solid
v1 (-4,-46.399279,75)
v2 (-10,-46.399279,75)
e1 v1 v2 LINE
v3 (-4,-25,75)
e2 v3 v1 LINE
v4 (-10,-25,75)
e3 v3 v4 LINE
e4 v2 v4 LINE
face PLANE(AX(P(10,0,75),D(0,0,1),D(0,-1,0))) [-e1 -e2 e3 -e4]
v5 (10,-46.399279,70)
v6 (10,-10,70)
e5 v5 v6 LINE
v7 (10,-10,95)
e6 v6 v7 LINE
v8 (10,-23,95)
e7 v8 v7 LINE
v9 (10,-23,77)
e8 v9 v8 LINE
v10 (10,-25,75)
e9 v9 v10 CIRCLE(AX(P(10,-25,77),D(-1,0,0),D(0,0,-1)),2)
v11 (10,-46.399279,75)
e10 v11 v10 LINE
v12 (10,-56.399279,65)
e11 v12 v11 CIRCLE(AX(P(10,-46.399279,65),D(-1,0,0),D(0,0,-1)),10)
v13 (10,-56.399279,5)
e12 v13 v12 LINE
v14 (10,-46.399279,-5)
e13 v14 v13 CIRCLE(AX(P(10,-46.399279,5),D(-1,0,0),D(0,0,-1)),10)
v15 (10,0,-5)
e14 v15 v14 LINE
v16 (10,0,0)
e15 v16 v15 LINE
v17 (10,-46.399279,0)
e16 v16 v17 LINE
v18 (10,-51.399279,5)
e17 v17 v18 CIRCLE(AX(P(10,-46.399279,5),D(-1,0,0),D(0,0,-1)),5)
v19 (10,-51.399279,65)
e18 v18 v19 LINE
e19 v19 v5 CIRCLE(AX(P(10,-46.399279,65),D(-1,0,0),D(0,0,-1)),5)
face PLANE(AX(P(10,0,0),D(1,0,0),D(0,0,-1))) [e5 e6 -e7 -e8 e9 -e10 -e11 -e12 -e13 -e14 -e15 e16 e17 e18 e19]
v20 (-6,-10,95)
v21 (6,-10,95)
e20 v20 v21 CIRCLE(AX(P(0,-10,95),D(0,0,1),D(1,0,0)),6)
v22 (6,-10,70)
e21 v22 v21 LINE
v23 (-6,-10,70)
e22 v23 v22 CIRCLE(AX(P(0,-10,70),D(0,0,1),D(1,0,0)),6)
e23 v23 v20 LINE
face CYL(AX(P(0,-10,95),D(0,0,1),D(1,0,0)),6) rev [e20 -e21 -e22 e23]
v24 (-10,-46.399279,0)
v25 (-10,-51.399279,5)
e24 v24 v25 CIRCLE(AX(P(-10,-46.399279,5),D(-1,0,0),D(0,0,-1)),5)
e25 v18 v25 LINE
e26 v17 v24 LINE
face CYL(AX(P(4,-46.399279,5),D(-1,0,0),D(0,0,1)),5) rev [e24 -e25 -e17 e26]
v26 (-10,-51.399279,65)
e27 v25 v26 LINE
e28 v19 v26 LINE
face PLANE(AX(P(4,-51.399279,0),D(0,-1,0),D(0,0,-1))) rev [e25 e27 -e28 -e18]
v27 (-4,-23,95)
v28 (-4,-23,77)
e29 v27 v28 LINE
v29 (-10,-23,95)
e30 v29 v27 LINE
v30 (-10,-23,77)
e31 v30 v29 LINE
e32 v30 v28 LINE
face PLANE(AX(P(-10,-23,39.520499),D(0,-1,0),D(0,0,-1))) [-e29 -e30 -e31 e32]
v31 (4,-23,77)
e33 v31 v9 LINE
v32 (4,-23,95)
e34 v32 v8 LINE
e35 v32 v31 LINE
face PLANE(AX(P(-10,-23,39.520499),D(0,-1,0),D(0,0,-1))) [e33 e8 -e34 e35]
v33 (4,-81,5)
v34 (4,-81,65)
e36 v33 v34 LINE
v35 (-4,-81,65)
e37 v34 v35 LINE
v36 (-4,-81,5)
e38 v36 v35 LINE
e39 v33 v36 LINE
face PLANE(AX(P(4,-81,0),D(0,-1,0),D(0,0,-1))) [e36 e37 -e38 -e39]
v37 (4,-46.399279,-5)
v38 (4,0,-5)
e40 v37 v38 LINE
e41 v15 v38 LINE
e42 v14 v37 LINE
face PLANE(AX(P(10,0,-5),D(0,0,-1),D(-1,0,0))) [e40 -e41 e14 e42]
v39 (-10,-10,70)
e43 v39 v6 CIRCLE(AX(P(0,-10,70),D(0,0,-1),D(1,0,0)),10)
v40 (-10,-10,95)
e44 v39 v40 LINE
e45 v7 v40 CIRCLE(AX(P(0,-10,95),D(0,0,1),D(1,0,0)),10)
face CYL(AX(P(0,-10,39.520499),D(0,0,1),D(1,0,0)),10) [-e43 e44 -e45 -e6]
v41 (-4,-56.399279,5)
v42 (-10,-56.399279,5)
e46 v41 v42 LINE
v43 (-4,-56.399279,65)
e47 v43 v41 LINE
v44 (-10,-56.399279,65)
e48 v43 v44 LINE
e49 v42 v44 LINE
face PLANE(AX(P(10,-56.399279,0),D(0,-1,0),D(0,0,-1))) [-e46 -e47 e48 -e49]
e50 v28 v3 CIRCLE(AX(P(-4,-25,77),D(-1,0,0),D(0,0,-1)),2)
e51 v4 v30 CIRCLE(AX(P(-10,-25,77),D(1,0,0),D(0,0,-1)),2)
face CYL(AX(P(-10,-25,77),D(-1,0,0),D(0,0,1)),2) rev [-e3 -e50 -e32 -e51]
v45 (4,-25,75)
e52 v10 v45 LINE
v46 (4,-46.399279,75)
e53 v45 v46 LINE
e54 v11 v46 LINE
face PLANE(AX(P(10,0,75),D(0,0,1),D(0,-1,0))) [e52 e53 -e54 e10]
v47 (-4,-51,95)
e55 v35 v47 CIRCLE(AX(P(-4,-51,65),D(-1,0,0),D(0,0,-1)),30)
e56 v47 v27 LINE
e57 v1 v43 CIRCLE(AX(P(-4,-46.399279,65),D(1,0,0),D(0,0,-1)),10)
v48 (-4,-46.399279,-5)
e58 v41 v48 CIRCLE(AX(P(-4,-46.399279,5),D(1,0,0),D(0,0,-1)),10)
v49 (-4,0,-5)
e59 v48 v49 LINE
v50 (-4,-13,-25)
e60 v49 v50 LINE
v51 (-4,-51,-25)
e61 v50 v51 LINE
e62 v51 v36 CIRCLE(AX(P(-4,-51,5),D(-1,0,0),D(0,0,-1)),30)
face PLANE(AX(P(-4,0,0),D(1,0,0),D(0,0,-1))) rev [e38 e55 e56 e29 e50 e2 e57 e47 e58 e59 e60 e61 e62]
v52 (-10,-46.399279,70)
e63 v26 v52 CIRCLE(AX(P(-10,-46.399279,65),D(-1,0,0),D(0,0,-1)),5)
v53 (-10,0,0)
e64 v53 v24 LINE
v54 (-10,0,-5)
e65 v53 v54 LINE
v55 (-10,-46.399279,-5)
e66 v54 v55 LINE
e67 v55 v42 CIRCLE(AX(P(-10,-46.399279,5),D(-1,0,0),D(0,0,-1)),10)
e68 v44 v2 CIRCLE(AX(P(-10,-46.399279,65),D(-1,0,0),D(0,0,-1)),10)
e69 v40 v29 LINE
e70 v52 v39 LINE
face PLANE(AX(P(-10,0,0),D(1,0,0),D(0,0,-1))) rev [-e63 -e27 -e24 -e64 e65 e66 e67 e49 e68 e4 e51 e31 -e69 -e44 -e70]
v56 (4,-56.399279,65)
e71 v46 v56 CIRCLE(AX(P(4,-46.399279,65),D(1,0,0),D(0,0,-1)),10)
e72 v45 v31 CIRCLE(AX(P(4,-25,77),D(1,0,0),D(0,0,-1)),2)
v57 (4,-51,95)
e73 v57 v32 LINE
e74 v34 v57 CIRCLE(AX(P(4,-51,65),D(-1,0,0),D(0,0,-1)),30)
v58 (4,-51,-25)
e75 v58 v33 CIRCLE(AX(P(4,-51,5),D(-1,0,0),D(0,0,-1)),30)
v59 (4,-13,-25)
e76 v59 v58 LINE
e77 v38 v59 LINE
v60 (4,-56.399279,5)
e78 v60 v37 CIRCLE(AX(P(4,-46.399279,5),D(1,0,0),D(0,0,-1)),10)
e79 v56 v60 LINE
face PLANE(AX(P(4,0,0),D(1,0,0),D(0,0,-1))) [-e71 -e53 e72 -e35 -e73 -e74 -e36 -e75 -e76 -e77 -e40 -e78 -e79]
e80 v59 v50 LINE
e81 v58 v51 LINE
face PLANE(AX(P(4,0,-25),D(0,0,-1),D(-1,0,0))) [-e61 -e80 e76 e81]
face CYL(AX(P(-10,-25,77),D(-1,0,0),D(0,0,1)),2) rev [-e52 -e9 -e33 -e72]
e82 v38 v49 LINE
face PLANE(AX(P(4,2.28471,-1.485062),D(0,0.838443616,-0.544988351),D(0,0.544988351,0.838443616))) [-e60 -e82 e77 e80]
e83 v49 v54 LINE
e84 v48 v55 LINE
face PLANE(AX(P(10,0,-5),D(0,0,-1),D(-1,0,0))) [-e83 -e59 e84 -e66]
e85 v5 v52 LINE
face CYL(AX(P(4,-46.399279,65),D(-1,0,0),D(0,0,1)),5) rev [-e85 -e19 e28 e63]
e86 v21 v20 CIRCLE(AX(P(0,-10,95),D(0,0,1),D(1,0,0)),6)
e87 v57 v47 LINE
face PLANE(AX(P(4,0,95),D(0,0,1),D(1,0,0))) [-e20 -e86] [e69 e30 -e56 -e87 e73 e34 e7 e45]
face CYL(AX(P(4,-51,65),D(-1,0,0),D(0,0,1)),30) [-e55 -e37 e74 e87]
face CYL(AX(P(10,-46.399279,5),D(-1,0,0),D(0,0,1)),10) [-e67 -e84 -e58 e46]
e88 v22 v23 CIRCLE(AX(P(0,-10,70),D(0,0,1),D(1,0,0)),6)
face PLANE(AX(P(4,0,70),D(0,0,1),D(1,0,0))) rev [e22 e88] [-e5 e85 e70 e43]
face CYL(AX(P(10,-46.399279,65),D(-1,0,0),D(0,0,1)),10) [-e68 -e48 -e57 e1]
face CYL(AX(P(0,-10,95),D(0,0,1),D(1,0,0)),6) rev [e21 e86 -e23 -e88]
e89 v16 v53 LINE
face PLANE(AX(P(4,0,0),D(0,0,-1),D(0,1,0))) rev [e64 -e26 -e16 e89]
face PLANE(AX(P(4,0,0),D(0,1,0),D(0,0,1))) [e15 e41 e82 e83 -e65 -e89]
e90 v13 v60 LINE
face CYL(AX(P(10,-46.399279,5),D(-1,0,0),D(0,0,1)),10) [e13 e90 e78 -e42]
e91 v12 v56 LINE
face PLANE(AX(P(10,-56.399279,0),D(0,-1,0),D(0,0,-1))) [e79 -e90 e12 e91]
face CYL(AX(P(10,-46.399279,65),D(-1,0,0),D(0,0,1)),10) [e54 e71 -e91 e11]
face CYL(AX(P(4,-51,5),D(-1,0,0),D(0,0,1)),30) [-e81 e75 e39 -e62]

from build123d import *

# Parameters (mm, degrees)
FRAME_PLATE_8MM_DEPTH      = 4
FRAME_RIM_8MM_DEPTH        = 4
FRAME_FLANGE_20MM_DEPTH    = 10
SCREW_BOSS_DEPTH           = 25
RELIEF_CHANNEL_CUT_DEPTH   = 25
M12X1_5_TAPPED_HOLE1_D     = 12
M12X1_5_TAPPED_HOLE1_DEPTH = 25
EDGE_FILLET_R2_R           = 2


with BuildPart() as part:
    # Frame Profile Sketch → Frame Plate 8mm (new, symmetric)
    with BuildSketch(Plane(origin=(0, 0, 0), x_dir=(0, 0, -1), z_dir=(1, 0, 0))):
        with BuildLine():
            ThreePointArc((-65, -81), (-86.213203436, -72.213203436), (-95, -51))
            Line((-95, -51), (-95, 0))
            Line((-95, 0), (-75, 0))
            Line((-75, 0), (-75, -46.399278983))
            ThreePointArc((-75, -46.399278983), (-72.071067812, -53.470346795), (-65, -56.399278983))
            Line((-65, -56.399278983), (-5, -56.399278983))
            ThreePointArc((-5, -56.399278983), (2.071067812, -53.470346795), (5, -46.399278983))
            Line((5, -46.399278983), (5, 0))
            Line((5, 0), (25, -13))
            Line((25, -13), (25, -51))
            ThreePointArc((25, -51), (16.213203436, -72.213203436), (-5, -81))
            Line((-5, -81), (-65, -81))
        make_face()
    extrude(amount=FRAME_PLATE_8MM_DEPTH, both=True)

    # Sketch1_3 → Frame Rim 8mm (add, symmetric)
    with BuildSketch(Plane(origin=(0, 0, 0), x_dir=(0, 0, -1), z_dir=(1, 0, 0))):
        with BuildLine():
            ThreePointArc((-65, -56.399278983), (-72.071067812, -53.470346795), (-75, -46.399278983))
            Line((-75, -46.399278983), (-75, 0))
            Line((-75, 0), (-70, 0))
            Line((-70, 0), (-70, -46.399278983))
            ThreePointArc((-70, -46.399278983), (-68.535533906, -49.934812889), (-65, -51.399278983))
            Line((-65, -51.399278983), (-5, -51.399278983))
            ThreePointArc((-5, -51.399278983), (-1.464466094, -49.934812889), (0, -46.399278983))
            Line((0, -46.399278983), (0, 0))
            Line((0, 0), (5, 0))
            Line((5, 0), (5, -46.399278983))
            ThreePointArc((5, -46.399278983), (2.071067812, -53.470346795), (-5, -56.399278983))
            Line((-5, -56.399278983), (-65, -56.399278983))
        make_face()
    extrude(amount=FRAME_RIM_8MM_DEPTH, both=True)

    # Sketch1_4 → Frame Flange 20mm (add, symmetric)
    with BuildSketch(Plane(origin=(0, 0, 0), x_dir=(0, 0, -1), z_dir=(1, 0, 0))):
        with BuildLine():
            ThreePointArc((-65, -56.399278983), (-72.071067812, -53.470346795), (-75, -46.399278983))
            Line((-75, -46.399278983), (-75, 0))
            Line((-75, 0), (-70, 0))
            Line((-70, 0), (-70, -46.399278983))
            ThreePointArc((-70, -46.399278983), (-68.535533906, -49.934812889), (-65, -51.399278983))
            Line((-65, -51.399278983), (-5, -51.399278983))
            ThreePointArc((-5, -51.399278983), (-1.464466094, -49.934812889), (0, -46.399278983))
            Line((0, -46.399278983), (0, 0))
            Line((0, 0), (5, 0))
            Line((5, 0), (5, -46.399278983))
            ThreePointArc((5, -46.399278983), (2.071067812, -53.470346795), (-5, -56.399278983))
            Line((-5, -56.399278983), (-65, -56.399278983))
        make_face()
    extrude(amount=FRAME_FLANGE_20MM_DEPTH, both=True)

    # Screw Boss Sketch → Screw Boss (add)
    with BuildSketch(Plane.XY.offset(95)):
        with BuildLine():
            Line((-10, -10), (-10, -23))
            Line((-10, -23), (10, -23))
            Line((10, -23), (10, -10))
            ThreePointArc((10, -10), (0, 0), (-10, -10))
        make_face()
    extrude(amount=-SCREW_BOSS_DEPTH)

    # Relief Channel Sketch → Relief Channel Cut (cut)
    with BuildSketch(Plane.XY.offset(95)):
        with BuildLine():
            Line((-10, 0), (-4, 0))
            Line((-4, 0), (-4, -0.83484861))
            ThreePointArc((-4, -0.83484861), (-8.366600265, -4.522774425), (-10, -10))
            Line((-10, -10), (-10, 0))
        make_face()
        with BuildLine():
            Line((-4, 0), (-4, -0.83484861))
            ThreePointArc((-4, -0.83484861), (-2.043096424, -0.210936868), (2.7e-08, 0))
            Line((2.7e-08, 0), (-4, 0))
        make_face()
        with BuildLine():
            Line((4, 0), (2.7e-08, 0))
            ThreePointArc((2.7e-08, 0), (2.04309645, -0.210936873), (4, -0.83484861))
            Line((4, -0.83484861), (4, 0))
        make_face()
        with BuildLine():
            Line((10, -10), (10, 0))
            Line((10, 0), (4, 0))
            Line((4, 0), (4, -0.83484861))
            ThreePointArc((4, -0.83484861), (8.366600265, -4.522774425), (10, -10))
        make_face()
    extrude(amount=-RELIEF_CHANNEL_CUT_DEPTH, mode=Mode.SUBTRACT)

    # M12x1.5 Tapped Hole1
    with Locations(Plane.XY.offset(95)):
        with Locations((0, -10)):
            Hole(M12X1_5_TAPPED_HOLE1_D / 2, depth=M12X1_5_TAPPED_HOLE1_DEPTH)

    # Edge Fillet R2
    edge_fillet_r2_edges = [part.edges().sort_by_distance(p)[0] for p in [
        (-7, -23, 75),
        (7, -23, 75),
    ]]
    fillet(edge_fillet_r2_edges, radius=EDGE_FILLET_R2_R)


solid = part.part
